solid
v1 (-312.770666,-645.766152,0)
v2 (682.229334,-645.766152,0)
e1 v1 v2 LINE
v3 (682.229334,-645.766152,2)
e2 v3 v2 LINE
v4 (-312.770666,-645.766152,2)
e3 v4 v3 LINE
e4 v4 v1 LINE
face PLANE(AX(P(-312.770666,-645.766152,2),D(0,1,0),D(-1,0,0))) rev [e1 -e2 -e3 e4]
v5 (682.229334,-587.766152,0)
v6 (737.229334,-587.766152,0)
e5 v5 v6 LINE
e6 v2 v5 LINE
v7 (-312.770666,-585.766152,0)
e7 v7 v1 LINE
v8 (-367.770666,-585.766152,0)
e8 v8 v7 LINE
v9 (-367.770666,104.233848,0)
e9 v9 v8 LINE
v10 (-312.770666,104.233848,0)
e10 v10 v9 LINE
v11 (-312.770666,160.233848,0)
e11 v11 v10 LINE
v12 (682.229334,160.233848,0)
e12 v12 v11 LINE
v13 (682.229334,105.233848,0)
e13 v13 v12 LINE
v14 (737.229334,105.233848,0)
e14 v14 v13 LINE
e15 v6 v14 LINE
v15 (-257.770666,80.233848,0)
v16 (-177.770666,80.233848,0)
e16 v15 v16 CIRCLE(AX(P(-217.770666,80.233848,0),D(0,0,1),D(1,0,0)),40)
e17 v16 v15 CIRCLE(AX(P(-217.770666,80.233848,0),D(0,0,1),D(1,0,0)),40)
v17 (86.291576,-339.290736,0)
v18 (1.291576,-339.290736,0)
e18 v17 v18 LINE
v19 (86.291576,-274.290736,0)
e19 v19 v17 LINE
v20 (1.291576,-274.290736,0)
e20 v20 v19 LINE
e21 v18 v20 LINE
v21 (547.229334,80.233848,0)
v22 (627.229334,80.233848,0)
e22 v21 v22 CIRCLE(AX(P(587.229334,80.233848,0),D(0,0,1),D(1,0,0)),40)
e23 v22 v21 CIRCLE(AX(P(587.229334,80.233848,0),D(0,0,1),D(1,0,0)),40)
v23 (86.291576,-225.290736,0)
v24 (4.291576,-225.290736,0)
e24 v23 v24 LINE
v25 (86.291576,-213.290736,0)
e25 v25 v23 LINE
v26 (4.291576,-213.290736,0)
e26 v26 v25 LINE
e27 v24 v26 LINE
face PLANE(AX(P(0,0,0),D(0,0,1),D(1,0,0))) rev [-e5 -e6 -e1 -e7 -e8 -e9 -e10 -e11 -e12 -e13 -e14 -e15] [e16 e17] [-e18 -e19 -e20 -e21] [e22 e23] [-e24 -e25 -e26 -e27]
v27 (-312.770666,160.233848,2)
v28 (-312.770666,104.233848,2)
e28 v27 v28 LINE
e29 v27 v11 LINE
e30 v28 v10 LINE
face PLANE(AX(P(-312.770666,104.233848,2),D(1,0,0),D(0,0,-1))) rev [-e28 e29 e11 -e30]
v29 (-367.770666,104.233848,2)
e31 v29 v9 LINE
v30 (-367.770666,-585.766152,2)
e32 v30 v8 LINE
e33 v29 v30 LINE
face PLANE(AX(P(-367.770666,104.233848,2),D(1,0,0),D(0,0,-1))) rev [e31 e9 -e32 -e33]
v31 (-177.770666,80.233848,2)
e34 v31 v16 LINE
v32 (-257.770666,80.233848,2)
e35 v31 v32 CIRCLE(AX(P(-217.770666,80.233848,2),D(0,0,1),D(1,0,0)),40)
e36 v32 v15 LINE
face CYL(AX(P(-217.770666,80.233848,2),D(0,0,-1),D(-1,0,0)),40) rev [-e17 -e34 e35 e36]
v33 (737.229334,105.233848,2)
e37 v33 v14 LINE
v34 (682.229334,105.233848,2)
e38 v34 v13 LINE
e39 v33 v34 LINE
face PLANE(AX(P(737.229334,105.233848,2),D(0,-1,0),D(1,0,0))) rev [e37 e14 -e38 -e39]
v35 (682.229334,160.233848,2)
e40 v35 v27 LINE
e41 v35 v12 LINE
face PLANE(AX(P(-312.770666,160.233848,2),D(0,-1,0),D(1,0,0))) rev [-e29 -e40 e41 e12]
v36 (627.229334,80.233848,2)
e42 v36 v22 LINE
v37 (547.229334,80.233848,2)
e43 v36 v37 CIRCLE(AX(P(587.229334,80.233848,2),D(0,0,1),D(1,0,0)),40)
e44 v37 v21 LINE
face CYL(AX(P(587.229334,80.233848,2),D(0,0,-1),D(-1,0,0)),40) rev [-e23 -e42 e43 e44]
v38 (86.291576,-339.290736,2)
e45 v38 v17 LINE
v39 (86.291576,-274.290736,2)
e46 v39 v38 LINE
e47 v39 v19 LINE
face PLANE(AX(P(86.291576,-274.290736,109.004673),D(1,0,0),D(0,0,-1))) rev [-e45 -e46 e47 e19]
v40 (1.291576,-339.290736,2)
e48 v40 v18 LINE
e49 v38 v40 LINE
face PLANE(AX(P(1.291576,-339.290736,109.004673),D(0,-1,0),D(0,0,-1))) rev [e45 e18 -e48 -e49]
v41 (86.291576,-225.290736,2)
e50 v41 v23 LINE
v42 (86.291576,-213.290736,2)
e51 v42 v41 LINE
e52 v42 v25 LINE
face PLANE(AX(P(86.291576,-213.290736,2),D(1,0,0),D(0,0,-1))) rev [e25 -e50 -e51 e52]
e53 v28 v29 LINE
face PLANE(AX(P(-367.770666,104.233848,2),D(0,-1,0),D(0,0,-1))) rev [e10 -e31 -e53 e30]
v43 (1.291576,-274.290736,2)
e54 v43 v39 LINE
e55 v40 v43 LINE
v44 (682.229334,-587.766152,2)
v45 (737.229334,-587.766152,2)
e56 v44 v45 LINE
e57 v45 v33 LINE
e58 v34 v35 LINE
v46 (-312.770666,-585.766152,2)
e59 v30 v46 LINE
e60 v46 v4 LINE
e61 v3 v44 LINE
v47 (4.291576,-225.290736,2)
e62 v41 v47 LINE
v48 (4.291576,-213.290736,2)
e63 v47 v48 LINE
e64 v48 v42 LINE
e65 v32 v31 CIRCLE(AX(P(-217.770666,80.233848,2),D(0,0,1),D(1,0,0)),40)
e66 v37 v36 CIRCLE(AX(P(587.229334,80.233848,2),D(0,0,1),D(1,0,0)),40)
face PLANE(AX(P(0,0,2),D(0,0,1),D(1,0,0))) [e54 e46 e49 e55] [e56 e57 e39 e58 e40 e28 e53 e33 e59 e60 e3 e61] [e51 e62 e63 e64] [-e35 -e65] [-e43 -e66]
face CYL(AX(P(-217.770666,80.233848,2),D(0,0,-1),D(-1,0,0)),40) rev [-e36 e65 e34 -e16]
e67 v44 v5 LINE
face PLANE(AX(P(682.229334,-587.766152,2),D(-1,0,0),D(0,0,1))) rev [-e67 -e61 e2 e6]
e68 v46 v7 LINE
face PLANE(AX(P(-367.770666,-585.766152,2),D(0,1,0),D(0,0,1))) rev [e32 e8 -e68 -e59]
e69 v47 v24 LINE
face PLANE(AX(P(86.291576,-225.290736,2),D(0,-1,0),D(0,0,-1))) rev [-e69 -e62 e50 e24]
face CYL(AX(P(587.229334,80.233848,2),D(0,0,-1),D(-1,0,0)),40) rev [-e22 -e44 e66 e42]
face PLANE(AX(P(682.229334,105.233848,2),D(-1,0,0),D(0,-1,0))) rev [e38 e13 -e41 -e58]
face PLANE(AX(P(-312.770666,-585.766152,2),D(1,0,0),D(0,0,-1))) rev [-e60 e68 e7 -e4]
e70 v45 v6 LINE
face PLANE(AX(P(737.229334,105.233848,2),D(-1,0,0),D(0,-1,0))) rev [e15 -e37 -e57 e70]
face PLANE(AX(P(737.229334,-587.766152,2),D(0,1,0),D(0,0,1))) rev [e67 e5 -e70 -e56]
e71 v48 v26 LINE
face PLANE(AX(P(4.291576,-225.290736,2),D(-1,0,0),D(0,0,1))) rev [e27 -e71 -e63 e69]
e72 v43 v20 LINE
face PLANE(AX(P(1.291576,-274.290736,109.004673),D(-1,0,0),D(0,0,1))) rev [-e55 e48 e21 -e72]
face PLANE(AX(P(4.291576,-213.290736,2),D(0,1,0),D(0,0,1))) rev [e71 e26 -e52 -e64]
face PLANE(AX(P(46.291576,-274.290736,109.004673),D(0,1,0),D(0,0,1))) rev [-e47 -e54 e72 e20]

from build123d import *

# Parameters (mm, degrees)
SKETCH_1_R          = 40
EXTRUDE_1_DEPTH     = 2
SKETCH_3_W          = 12
SKETCH_3_H          = 82
CUT_EXTRUDE_2_DEPTH = 2
CUT_EXTRUDE_3_DEPTH = 2


with BuildPart() as part:
    # 草图1 → 凸台-拉伸1 (new body)
    with BuildSketch(Plane.XY):
        Polygon((-367.770666468, 104.233847936), (-312.770666468, 104.233847936), (-312.770666468, 160.233847936), (682.229333532, 160.233847936), (682.229333532, 105.233847936), (737.229333532, 105.233847936), (737.229333532, -587.766152064), (682.229333532, -587.766152064), (682.229333532, -645.766152064), (-312.770666468, -645.766152064), (-312.770666468, -585.766152064), (-367.770666468, -585.766152064), align=None)
        with Locations((-217.770666468, 80.233847936)):
            Circle(SKETCH_1_R, mode=Mode.SUBTRACT)
        with Locations((587.229333532, 80.233847936)):
            Circle(SKETCH_1_R, mode=Mode.SUBTRACT)
    extrude(amount=EXTRUDE_1_DEPTH)

    # 草图3 → 切除-拉伸2 (cut)
    with BuildSketch(Plane(origin=(995.435508438, 654.453268367, 0), x_dir=(0, -1, 0), z_dir=(0, 0, -1))):
        with Locations((873.744003867, 950.143932906)):
            Rectangle(SKETCH_3_W, SKETCH_3_H)
    extrude(amount=-CUT_EXTRUDE_2_DEPTH, mode=Mode.SUBTRACT)

    # 草图4 → 切除-拉伸3 (cut)
    with BuildSketch(Plane(origin=(995.435508438, 654.453268367, 0), x_dir=(0, -1, 0), z_dir=(0, 0, -1))):
        Polygon((928.744003867, 949.143932916), (928.744003867, 909.143932916), (993.744003867, 909.143932916), (993.744003867, 949.143932916), (993.744003867, 994.143932916), (928.744003867, 994.143932916), align=None)
    extrude(amount=-CUT_EXTRUDE_3_DEPTH, mode=Mode.SUBTRACT)


solid = part.part
